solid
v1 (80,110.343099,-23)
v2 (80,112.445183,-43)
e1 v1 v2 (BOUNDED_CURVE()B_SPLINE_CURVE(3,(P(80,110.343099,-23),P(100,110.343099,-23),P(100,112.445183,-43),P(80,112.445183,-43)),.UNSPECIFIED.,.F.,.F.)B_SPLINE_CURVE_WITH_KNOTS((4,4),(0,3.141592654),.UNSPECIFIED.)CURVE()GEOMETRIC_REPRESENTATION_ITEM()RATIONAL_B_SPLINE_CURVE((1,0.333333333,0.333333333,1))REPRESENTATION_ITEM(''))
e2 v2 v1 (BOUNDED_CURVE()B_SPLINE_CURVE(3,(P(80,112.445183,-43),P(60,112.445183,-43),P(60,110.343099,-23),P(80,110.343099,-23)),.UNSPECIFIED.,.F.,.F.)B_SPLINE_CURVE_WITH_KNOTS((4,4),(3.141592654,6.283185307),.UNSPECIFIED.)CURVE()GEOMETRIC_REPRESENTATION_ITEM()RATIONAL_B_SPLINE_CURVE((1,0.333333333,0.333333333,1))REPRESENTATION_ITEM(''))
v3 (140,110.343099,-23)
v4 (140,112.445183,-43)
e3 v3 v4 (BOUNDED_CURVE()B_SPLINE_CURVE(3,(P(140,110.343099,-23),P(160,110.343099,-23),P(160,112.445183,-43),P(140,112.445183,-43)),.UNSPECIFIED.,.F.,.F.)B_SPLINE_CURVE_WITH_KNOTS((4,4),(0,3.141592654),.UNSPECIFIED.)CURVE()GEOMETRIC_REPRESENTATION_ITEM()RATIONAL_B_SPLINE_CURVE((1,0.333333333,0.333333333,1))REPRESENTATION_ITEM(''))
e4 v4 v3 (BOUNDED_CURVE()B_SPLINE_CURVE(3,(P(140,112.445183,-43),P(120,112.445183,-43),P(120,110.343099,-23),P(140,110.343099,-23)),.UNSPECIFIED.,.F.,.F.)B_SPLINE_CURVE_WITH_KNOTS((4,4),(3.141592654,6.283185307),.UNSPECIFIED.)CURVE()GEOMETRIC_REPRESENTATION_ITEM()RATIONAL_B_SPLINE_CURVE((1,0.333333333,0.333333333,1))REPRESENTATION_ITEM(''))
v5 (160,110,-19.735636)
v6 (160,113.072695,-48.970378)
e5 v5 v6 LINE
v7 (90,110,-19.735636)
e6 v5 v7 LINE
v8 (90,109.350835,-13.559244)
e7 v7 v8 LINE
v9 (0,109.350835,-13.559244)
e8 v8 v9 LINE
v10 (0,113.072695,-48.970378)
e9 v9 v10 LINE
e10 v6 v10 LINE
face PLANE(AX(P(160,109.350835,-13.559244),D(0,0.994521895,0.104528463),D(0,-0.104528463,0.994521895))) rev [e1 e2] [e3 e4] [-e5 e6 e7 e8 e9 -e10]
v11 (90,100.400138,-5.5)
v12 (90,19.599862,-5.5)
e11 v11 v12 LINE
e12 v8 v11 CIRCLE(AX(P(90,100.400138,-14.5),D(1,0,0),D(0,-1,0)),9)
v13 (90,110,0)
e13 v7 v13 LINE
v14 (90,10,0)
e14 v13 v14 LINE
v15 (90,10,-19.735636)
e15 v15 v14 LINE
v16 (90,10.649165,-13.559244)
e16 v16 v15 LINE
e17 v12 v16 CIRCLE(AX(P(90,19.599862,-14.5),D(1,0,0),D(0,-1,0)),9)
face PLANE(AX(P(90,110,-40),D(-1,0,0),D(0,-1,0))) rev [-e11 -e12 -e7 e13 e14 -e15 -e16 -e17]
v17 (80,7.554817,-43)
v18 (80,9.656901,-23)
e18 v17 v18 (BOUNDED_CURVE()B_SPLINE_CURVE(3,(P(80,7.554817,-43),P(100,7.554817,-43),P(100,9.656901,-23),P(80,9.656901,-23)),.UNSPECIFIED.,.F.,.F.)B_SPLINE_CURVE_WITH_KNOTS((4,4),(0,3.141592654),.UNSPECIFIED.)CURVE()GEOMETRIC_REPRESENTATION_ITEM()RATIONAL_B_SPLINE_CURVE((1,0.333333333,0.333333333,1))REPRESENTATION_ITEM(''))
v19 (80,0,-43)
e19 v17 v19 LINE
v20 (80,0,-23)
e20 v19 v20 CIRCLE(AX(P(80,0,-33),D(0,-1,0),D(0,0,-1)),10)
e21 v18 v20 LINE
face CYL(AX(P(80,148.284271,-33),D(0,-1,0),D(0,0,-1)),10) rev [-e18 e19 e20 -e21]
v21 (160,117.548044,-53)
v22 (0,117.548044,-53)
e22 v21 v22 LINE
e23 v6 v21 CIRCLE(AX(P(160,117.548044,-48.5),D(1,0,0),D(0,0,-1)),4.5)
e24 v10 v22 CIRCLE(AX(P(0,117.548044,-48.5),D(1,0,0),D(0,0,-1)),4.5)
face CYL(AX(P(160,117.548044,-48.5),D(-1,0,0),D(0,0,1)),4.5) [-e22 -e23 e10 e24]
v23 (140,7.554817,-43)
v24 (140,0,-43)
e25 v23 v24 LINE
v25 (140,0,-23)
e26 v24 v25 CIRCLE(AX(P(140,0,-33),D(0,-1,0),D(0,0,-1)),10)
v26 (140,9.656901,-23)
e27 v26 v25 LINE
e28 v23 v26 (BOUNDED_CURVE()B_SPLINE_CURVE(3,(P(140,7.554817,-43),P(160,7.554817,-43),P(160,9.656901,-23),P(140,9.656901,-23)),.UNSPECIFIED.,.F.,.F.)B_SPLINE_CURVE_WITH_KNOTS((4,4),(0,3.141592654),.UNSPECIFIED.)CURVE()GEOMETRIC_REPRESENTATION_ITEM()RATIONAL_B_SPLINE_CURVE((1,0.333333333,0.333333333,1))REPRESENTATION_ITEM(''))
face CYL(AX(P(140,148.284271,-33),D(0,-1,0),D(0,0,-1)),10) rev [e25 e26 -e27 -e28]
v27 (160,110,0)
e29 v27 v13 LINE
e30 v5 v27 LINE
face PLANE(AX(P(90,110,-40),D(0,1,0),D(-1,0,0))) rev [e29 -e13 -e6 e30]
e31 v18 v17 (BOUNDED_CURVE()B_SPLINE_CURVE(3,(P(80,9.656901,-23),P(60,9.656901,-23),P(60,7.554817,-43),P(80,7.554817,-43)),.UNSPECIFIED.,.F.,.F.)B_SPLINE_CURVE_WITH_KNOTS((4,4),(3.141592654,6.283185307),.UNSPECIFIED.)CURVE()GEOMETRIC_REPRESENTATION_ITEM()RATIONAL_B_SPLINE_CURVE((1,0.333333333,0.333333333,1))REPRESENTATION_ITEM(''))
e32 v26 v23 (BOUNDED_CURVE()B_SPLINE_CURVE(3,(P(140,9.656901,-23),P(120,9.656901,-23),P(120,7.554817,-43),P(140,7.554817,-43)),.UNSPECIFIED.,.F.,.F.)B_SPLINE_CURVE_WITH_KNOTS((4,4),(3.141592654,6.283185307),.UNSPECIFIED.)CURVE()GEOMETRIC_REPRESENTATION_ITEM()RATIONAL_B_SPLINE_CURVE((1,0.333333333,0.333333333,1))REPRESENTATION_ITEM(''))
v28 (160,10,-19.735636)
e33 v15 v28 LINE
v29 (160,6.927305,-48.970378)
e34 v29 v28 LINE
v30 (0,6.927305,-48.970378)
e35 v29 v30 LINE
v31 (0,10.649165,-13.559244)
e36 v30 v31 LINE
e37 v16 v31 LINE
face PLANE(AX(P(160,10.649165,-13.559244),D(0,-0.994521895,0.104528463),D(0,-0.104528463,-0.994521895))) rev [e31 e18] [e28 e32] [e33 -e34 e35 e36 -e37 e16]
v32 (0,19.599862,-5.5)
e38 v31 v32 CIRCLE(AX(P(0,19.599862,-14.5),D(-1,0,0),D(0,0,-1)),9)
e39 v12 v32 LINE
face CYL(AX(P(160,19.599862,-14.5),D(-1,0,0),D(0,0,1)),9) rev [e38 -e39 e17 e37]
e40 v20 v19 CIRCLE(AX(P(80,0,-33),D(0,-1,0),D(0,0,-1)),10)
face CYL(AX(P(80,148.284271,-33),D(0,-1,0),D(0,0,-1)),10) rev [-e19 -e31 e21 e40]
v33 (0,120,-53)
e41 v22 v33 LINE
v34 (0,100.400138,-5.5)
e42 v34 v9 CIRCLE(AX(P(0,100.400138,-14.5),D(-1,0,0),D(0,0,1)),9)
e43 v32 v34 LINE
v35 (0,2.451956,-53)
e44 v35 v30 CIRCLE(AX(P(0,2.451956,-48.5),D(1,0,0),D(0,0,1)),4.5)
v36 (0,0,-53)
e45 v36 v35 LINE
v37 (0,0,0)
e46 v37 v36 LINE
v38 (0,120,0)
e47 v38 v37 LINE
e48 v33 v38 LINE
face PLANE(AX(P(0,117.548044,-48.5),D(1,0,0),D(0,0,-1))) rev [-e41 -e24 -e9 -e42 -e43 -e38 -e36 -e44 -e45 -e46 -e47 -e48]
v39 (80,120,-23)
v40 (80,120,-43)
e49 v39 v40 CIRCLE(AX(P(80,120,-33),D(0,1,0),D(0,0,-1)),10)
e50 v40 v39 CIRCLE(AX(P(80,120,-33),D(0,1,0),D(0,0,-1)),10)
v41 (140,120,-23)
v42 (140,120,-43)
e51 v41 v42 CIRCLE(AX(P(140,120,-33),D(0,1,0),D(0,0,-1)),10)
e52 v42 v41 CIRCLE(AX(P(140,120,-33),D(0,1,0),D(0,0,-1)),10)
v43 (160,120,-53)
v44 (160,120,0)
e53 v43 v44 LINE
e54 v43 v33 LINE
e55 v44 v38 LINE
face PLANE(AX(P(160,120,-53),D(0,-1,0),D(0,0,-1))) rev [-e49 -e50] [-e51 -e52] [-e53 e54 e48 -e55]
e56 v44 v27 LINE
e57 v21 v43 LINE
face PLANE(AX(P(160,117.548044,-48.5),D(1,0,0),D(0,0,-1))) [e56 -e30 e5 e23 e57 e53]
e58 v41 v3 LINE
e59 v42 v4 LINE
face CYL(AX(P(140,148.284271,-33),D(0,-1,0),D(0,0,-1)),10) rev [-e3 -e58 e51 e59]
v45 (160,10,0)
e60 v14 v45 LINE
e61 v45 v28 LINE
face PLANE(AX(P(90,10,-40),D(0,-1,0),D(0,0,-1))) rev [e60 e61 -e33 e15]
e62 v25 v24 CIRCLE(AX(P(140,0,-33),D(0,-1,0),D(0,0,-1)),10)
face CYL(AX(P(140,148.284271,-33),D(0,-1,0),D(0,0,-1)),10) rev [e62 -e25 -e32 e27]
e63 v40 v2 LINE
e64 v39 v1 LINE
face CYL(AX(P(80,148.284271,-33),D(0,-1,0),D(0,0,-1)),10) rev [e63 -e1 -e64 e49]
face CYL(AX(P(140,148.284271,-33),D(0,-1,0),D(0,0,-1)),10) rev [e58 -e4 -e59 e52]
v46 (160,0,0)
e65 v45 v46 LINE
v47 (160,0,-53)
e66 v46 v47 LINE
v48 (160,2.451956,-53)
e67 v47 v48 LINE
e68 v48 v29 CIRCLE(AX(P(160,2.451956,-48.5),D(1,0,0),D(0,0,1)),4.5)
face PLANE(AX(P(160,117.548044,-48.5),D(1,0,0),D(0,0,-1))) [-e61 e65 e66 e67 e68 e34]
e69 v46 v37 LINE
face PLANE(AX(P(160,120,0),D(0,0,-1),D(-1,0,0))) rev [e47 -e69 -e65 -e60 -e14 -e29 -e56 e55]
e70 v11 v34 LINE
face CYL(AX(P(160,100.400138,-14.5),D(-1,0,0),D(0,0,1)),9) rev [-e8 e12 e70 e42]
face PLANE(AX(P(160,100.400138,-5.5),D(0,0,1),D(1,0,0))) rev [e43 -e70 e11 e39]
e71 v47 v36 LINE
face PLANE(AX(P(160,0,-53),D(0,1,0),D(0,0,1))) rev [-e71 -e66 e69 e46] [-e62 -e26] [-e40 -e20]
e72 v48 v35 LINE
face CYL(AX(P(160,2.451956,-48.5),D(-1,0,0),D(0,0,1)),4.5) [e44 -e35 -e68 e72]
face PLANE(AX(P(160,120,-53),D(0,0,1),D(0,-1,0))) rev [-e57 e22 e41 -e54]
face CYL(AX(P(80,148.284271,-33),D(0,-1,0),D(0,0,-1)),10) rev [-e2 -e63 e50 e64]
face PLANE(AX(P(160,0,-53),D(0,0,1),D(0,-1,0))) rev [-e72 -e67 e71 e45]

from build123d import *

# Parameters (mm, degrees)
MEMBER_C_12_1_DEPTH = 160
SKETCH_2_W          = 100
SKETCH_2_H          = 100
CUT_EXTRUDE_1_DEPTH = 40
CUT_EXTRUDE_2_REACH = 208.903
SKETCH_3_R          = 10


with BuildPart() as part:
    # Sketch11 → Member C _ 12_1 (new body)
    with BuildSketch(Plane(origin=(0, 0, 0), x_dir=(0, 0, -1), z_dir=(1, 0, 0))):
        with BuildLine():
            Line((53, 120), (0, 120))
            Line((0, 120), (0, 0))
            Line((0, 0), (53, 0))
            Line((53, 0), (53, 2.451956213))
            ThreePointArc((53, 2.451956213), (51.844151715, 5.463043942), (48.970378085, 6.927304742))
            Line((48.970378085, 6.927304742), (13.559243831, 10.649164928))
            ThreePointArc((13.559243831, 10.649164928), (7.811696571, 13.577686529), (5.5, 19.599861986))
            Line((5.5, 19.599861986), (5.5, 100.400138014))
            ThreePointArc((5.5, 100.400138014), (7.811696571, 106.422313471), (13.559243831, 109.350835072))
            Line((13.559243831, 109.350835072), (48.970378085, 113.072695258))
            ThreePointArc((48.970378085, 113.072695258), (51.844151715, 114.536956058), (53, 117.548043787))
            Line((53, 117.548043787), (53, 120))
        make_face()
    extrude(amount=MEMBER_C_12_1_DEPTH)

    # 草图2 → 切除-拉伸1 (cut)
    with BuildSketch(Plane.XY):
        with Locations((140, 60)):
            Rectangle(SKETCH_2_W, SKETCH_2_H)
    extrude(amount=-CUT_EXTRUDE_1_DEPTH, mode=Mode.SUBTRACT)

    # 切除-拉伸2: up to this face of the body (flat: up to its plane)
    cut_extrude_2_end = Plane(part.part.faces().sort_by_distance((80, 120, -26.5))[0])
    # 草图3 → 切除-拉伸2 (cut, up to the picked face)
    with BuildSketch(Plane.XZ, mode=Mode.PRIVATE) as cut_extrude_2_sk1:
        with Locations(Location((140, -33, 0), (0, 0, 270))):
            Circle(SKETCH_3_R)
    cut_extrude_2_tool1 = split(extrude(cut_extrude_2_sk1.sketch, amount=-CUT_EXTRUDE_2_REACH, mode=Mode.PRIVATE), bisect_by=cut_extrude_2_end, keep=Keep.BOTH, mode=Mode.PRIVATE)
    # 草图3 → 切除-拉伸2 (cut, up to the picked face)
    with BuildSketch(Plane.XZ, mode=Mode.PRIVATE) as cut_extrude_2_sk2:
        with Locations(Location((80, -33, 0), (0, 0, 270))):
            Circle(SKETCH_3_R)
    cut_extrude_2_tool2 = split(extrude(cut_extrude_2_sk2.sketch, amount=-CUT_EXTRUDE_2_REACH, mode=Mode.PRIVATE), bisect_by=cut_extrude_2_end, keep=Keep.BOTH, mode=Mode.PRIVATE)
    add(cut_extrude_2_tool1.solids().sort_by(Axis((140, 0, -33), (0, 1, 0)))[0], mode=Mode.SUBTRACT)
    add(cut_extrude_2_tool2.solids().sort_by(Axis((80, 0, -33), (0, 1, 0)))[0], mode=Mode.SUBTRACT)


solid = part.part
